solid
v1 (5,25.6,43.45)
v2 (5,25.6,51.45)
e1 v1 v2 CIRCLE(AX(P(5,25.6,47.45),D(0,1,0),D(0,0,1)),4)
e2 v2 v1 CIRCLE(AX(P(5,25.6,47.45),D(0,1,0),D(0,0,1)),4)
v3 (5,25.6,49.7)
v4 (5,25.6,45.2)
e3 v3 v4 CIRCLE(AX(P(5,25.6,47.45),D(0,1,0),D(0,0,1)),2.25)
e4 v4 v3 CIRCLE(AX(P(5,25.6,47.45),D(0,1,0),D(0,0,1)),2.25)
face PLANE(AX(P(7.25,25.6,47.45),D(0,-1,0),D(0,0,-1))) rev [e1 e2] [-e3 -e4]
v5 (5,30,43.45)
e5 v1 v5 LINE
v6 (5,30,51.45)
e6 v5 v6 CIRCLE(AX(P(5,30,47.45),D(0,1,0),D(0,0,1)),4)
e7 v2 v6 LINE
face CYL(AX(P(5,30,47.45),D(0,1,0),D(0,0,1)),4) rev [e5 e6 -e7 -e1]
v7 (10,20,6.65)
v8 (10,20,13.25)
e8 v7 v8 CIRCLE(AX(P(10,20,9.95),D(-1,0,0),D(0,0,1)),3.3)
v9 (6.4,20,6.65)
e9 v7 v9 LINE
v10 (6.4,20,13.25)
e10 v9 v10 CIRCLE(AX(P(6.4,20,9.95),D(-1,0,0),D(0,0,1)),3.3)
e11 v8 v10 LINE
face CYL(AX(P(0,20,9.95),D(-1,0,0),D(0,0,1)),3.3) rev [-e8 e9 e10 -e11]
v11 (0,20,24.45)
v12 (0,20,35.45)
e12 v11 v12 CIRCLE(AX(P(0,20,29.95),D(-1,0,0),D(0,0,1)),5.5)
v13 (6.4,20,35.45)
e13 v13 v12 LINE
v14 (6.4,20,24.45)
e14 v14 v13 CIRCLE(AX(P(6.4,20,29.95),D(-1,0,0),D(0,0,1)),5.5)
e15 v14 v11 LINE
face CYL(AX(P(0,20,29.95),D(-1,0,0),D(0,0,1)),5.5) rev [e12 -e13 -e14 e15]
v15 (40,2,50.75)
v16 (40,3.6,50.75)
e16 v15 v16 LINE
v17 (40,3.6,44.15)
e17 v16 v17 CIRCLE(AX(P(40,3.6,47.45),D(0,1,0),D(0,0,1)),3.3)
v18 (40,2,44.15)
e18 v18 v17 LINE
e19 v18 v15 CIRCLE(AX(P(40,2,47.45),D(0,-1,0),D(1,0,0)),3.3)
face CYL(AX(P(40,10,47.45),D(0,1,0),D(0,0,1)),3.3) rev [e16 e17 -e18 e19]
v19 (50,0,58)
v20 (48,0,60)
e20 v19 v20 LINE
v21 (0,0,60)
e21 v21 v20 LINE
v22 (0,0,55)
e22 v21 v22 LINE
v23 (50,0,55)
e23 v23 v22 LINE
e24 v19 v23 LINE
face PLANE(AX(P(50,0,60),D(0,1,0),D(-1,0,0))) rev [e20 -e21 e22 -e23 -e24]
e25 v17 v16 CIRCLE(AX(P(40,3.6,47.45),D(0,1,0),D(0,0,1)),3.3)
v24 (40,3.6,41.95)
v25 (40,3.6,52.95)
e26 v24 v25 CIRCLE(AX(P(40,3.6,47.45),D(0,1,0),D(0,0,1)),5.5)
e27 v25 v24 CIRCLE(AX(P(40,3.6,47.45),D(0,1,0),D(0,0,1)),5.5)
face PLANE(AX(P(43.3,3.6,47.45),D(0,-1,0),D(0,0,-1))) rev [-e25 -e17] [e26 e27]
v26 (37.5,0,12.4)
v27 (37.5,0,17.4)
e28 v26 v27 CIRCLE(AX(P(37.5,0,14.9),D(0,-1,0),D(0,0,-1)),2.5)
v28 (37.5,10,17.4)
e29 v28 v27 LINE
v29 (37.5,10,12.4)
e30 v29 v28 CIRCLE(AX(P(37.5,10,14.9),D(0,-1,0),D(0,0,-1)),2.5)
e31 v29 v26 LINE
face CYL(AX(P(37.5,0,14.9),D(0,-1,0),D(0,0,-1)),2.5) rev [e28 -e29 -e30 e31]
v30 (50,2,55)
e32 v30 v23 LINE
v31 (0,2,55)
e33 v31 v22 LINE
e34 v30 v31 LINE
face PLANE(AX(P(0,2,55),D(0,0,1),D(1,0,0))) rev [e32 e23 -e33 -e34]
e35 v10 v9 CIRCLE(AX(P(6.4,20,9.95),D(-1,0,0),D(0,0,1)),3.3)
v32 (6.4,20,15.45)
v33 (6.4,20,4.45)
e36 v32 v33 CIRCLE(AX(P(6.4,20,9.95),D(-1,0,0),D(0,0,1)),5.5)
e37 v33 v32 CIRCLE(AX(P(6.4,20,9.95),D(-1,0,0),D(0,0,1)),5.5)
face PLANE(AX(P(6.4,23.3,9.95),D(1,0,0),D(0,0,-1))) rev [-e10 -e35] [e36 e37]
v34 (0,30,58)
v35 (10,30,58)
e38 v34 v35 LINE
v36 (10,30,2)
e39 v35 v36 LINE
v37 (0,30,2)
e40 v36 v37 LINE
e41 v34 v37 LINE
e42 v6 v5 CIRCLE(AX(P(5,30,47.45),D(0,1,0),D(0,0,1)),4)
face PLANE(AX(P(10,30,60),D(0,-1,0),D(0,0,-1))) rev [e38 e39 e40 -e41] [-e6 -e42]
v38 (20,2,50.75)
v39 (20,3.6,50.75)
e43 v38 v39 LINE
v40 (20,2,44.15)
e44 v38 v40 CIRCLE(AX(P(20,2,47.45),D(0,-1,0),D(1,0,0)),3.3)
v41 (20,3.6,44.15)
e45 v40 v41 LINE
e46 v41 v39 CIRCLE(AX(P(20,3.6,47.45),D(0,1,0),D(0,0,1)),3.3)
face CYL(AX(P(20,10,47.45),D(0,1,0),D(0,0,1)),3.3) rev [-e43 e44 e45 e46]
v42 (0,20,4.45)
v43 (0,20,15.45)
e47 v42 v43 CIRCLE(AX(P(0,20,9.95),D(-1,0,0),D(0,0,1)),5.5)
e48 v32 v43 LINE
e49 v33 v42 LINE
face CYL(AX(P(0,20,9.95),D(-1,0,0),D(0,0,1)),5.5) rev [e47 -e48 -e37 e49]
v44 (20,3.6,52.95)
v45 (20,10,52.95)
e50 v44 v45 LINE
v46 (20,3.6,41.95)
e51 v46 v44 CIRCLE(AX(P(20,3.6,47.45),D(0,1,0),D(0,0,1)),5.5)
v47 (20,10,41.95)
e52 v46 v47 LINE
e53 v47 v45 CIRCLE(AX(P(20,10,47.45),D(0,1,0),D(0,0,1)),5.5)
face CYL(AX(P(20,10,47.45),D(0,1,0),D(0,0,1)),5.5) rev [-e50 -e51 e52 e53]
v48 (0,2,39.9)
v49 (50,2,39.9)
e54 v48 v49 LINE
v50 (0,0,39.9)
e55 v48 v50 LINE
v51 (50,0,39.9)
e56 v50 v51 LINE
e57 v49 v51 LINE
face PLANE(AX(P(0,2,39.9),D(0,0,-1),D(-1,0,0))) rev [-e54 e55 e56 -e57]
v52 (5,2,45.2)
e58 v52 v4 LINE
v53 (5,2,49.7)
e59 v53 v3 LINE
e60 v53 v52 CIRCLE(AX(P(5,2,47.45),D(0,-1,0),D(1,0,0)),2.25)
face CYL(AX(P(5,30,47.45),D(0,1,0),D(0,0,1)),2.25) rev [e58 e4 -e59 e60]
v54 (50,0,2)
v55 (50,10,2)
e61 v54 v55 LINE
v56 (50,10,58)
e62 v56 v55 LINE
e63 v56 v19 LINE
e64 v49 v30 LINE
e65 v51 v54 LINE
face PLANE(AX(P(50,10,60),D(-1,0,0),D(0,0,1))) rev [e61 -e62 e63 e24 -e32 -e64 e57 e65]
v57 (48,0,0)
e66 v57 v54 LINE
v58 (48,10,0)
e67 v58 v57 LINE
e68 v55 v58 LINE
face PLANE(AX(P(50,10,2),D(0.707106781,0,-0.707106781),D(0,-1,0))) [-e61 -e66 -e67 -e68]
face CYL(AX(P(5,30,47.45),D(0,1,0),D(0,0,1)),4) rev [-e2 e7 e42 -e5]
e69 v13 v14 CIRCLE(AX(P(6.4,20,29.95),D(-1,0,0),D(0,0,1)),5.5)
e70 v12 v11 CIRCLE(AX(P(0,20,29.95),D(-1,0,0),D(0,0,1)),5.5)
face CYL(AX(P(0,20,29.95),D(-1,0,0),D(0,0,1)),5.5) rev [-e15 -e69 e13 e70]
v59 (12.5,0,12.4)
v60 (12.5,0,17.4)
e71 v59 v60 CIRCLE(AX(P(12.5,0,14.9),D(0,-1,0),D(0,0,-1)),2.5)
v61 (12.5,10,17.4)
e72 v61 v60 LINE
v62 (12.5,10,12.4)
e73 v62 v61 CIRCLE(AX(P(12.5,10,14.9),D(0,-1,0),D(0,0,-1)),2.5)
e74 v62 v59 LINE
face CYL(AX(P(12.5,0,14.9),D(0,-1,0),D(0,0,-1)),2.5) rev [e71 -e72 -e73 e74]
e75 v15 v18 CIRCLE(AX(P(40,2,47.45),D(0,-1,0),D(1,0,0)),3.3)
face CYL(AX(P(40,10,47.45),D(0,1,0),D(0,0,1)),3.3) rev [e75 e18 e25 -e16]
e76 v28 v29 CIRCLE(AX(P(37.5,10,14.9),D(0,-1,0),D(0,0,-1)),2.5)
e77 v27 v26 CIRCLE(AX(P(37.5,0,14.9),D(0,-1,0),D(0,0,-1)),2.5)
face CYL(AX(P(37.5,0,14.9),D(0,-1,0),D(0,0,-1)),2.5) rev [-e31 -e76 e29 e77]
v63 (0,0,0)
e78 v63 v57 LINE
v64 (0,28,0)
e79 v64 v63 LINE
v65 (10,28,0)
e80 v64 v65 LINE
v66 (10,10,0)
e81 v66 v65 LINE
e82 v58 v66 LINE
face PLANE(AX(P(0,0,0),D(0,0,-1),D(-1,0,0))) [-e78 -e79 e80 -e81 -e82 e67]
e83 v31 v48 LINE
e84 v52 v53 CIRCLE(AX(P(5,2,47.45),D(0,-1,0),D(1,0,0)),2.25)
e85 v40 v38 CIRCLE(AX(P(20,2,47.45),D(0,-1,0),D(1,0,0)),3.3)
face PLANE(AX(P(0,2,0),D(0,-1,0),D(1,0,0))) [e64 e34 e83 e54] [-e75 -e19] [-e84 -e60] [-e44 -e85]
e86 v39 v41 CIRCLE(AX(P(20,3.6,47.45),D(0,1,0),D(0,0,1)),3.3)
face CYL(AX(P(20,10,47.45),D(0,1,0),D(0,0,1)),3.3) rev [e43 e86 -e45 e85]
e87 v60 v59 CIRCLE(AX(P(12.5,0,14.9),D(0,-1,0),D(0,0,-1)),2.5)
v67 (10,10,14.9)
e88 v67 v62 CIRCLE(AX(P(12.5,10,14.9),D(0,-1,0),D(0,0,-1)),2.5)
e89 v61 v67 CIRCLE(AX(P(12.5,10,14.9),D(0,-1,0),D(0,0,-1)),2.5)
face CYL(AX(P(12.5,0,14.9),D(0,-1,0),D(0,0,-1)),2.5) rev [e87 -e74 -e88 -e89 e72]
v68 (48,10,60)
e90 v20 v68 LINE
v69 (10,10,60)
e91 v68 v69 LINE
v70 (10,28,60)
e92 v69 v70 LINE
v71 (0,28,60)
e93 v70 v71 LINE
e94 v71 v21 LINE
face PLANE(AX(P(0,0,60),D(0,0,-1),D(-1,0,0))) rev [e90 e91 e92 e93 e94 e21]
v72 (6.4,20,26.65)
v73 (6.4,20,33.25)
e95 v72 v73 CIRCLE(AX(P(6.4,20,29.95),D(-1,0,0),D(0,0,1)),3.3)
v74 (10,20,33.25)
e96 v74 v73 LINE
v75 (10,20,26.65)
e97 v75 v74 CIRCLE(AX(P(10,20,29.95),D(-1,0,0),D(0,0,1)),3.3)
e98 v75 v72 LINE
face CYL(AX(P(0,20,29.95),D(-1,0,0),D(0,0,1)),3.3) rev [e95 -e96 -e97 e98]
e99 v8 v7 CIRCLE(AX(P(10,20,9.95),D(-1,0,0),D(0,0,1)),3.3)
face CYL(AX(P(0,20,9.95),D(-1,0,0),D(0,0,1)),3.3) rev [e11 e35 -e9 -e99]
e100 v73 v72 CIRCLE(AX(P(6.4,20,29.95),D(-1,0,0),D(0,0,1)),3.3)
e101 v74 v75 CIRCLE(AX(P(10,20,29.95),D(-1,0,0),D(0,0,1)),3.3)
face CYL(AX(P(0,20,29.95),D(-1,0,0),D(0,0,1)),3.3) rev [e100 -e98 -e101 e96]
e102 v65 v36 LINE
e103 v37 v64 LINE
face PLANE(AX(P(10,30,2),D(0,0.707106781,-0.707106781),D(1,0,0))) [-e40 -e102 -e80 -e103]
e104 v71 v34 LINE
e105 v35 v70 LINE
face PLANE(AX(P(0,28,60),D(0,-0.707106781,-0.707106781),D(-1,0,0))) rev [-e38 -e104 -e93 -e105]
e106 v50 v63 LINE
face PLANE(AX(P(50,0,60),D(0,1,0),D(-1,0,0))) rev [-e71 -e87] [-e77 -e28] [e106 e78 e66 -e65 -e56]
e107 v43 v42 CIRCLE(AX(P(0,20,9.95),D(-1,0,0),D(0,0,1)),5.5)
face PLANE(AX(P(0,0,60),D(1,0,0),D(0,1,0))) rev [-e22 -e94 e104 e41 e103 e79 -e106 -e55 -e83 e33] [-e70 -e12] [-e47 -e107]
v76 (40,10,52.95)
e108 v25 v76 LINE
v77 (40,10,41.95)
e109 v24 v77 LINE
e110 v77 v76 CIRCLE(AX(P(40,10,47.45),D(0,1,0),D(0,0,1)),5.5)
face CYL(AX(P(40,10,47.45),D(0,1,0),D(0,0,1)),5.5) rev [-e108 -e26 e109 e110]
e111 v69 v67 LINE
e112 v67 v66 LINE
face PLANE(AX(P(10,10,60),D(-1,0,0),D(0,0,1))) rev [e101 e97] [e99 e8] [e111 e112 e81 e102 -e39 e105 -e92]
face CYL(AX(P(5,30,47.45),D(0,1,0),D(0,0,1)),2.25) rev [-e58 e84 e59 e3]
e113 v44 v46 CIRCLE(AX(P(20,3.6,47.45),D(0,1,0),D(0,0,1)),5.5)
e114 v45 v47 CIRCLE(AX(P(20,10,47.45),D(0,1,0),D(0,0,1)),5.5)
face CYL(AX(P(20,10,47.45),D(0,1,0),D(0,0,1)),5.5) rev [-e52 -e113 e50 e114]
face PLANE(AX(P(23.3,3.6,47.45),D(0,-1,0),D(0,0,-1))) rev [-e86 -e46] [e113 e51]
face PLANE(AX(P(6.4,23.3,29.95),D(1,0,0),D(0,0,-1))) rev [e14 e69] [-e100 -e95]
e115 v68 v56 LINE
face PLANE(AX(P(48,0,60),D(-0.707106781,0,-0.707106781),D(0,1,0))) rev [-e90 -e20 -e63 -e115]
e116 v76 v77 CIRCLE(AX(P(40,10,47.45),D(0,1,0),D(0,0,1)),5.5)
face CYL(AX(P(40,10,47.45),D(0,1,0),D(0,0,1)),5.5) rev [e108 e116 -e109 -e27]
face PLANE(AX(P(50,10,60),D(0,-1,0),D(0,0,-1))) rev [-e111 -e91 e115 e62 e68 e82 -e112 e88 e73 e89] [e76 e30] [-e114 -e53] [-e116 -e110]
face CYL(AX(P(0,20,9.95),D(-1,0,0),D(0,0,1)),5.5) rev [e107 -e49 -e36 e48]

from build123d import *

# Parameters (mm, degrees)
EXTRUDE_1_DEPTH              = 60
SKETCH_3_W                   = 50
SKETCH_3_H                   = 15.1
CUT_EXTRUDE_1_DEPTH          = 2
HOLE_WIZARD_M4_1_D           = 4.5
HOLE_WIZARD_M4_1_CBORE_D     = 8
HOLE_WIZARD_M4_1_CBORE_DEPTH = 4.4
HOLE_WIZARD_M6_1_D           = 6.6
HOLE_WIZARD_M6_1_CBORE_D     = 11
HOLE_WIZARD_M6_1_CBORE_DEPTH = 6.4
HOLE_WIZARD_M6_2_D           = 6.6
HOLE_WIZARD_M6_2_CBORE_D     = 11
HOLE_WIZARD_M6_2_CBORE_DEPTH = 6.4
CHAMFER_1_SIZE               = 2
HOLE_WIZARD_M6_1_2_D         = 5
HOLE_WIZARD_M6_1_2_DEPTH     = 17
HOLE_WIZARD_M6_1_2_TIP       = 1.502151548


with BuildPart() as part:
    # 草图2 → 凸台-拉伸1 (new body)
    with BuildSketch(Plane.XY):
        Polygon((50, 0), (0, 0), (0, 30), (10, 30), (10, 10), (50, 10), align=None)
    extrude(amount=EXTRUDE_1_DEPTH)

    # 草图3 → 切除-拉伸1 (cut)
    with BuildSketch(Plane.XZ):
        with Locations((25, 47.45)):
            Rectangle(SKETCH_3_W, SKETCH_3_H)
    extrude(amount=-CUT_EXTRUDE_1_DEPTH, mode=Mode.SUBTRACT)

    # M4 六角凹头螺钉的柱形沉头孔1 (through all)
    with Locations(Plane(origin=(-8.97546782, 30, 41.476708605), x_dir=(1, 0, 0), z_dir=(0, 1, 0))):
        with Locations((13.97546782, -5.973291395)):
            CounterBoreHole(HOLE_WIZARD_M4_1_D / 2, HOLE_WIZARD_M4_1_CBORE_D / 2, HOLE_WIZARD_M4_1_CBORE_DEPTH)

    # Hole Wizard M6 _1 (through all)
    with Locations(Plane(origin=(0, 10, 0), x_dir=(1, 0, 0), z_dir=(0, 1, 0))):
        with Locations((20, -47.45), (40, -47.45)):
            CounterBoreHole(HOLE_WIZARD_M6_1_D / 2, HOLE_WIZARD_M6_1_CBORE_D / 2, HOLE_WIZARD_M6_1_CBORE_DEPTH)

    # M6 六角凹头螺钉的柱形沉头孔2 (through all)
    with Locations(Plane.ZY):
        with Locations((9.95, 20), (29.95, 20)):
            CounterBoreHole(HOLE_WIZARD_M6_2_D / 2, HOLE_WIZARD_M6_2_CBORE_D / 2, HOLE_WIZARD_M6_2_CBORE_DEPTH)

    # 倒角1
    chamfer_1_edges = [part.edges().sort_by_distance(p)[0] for p in [
        (5, 30, 60),
        (50, 5, 60),
        (5, 30, 0),
        (50, 5, 0),
    ]]
    chamfer(chamfer_1_edges, length=CHAMFER_1_SIZE)

    # Hole Wizard M6 _1 2
    with Locations(Plane(origin=(0, 0, 0), x_dir=(-1, 0, 0), z_dir=(0, -1, 0))):
        with Locations((-12.5, -14.9), (-37.5, -14.9)):
            Hole(HOLE_WIZARD_M6_1_2_D / 2, depth=HOLE_WIZARD_M6_1_2_DEPTH)
            with Locations((0, 0, -(HOLE_WIZARD_M6_1_2_DEPTH + HOLE_WIZARD_M6_1_2_TIP / 2))):  # 118° drill point
                Cone(0, HOLE_WIZARD_M6_1_2_D / 2, HOLE_WIZARD_M6_1_2_TIP, mode=Mode.SUBTRACT)


solid = part.part
